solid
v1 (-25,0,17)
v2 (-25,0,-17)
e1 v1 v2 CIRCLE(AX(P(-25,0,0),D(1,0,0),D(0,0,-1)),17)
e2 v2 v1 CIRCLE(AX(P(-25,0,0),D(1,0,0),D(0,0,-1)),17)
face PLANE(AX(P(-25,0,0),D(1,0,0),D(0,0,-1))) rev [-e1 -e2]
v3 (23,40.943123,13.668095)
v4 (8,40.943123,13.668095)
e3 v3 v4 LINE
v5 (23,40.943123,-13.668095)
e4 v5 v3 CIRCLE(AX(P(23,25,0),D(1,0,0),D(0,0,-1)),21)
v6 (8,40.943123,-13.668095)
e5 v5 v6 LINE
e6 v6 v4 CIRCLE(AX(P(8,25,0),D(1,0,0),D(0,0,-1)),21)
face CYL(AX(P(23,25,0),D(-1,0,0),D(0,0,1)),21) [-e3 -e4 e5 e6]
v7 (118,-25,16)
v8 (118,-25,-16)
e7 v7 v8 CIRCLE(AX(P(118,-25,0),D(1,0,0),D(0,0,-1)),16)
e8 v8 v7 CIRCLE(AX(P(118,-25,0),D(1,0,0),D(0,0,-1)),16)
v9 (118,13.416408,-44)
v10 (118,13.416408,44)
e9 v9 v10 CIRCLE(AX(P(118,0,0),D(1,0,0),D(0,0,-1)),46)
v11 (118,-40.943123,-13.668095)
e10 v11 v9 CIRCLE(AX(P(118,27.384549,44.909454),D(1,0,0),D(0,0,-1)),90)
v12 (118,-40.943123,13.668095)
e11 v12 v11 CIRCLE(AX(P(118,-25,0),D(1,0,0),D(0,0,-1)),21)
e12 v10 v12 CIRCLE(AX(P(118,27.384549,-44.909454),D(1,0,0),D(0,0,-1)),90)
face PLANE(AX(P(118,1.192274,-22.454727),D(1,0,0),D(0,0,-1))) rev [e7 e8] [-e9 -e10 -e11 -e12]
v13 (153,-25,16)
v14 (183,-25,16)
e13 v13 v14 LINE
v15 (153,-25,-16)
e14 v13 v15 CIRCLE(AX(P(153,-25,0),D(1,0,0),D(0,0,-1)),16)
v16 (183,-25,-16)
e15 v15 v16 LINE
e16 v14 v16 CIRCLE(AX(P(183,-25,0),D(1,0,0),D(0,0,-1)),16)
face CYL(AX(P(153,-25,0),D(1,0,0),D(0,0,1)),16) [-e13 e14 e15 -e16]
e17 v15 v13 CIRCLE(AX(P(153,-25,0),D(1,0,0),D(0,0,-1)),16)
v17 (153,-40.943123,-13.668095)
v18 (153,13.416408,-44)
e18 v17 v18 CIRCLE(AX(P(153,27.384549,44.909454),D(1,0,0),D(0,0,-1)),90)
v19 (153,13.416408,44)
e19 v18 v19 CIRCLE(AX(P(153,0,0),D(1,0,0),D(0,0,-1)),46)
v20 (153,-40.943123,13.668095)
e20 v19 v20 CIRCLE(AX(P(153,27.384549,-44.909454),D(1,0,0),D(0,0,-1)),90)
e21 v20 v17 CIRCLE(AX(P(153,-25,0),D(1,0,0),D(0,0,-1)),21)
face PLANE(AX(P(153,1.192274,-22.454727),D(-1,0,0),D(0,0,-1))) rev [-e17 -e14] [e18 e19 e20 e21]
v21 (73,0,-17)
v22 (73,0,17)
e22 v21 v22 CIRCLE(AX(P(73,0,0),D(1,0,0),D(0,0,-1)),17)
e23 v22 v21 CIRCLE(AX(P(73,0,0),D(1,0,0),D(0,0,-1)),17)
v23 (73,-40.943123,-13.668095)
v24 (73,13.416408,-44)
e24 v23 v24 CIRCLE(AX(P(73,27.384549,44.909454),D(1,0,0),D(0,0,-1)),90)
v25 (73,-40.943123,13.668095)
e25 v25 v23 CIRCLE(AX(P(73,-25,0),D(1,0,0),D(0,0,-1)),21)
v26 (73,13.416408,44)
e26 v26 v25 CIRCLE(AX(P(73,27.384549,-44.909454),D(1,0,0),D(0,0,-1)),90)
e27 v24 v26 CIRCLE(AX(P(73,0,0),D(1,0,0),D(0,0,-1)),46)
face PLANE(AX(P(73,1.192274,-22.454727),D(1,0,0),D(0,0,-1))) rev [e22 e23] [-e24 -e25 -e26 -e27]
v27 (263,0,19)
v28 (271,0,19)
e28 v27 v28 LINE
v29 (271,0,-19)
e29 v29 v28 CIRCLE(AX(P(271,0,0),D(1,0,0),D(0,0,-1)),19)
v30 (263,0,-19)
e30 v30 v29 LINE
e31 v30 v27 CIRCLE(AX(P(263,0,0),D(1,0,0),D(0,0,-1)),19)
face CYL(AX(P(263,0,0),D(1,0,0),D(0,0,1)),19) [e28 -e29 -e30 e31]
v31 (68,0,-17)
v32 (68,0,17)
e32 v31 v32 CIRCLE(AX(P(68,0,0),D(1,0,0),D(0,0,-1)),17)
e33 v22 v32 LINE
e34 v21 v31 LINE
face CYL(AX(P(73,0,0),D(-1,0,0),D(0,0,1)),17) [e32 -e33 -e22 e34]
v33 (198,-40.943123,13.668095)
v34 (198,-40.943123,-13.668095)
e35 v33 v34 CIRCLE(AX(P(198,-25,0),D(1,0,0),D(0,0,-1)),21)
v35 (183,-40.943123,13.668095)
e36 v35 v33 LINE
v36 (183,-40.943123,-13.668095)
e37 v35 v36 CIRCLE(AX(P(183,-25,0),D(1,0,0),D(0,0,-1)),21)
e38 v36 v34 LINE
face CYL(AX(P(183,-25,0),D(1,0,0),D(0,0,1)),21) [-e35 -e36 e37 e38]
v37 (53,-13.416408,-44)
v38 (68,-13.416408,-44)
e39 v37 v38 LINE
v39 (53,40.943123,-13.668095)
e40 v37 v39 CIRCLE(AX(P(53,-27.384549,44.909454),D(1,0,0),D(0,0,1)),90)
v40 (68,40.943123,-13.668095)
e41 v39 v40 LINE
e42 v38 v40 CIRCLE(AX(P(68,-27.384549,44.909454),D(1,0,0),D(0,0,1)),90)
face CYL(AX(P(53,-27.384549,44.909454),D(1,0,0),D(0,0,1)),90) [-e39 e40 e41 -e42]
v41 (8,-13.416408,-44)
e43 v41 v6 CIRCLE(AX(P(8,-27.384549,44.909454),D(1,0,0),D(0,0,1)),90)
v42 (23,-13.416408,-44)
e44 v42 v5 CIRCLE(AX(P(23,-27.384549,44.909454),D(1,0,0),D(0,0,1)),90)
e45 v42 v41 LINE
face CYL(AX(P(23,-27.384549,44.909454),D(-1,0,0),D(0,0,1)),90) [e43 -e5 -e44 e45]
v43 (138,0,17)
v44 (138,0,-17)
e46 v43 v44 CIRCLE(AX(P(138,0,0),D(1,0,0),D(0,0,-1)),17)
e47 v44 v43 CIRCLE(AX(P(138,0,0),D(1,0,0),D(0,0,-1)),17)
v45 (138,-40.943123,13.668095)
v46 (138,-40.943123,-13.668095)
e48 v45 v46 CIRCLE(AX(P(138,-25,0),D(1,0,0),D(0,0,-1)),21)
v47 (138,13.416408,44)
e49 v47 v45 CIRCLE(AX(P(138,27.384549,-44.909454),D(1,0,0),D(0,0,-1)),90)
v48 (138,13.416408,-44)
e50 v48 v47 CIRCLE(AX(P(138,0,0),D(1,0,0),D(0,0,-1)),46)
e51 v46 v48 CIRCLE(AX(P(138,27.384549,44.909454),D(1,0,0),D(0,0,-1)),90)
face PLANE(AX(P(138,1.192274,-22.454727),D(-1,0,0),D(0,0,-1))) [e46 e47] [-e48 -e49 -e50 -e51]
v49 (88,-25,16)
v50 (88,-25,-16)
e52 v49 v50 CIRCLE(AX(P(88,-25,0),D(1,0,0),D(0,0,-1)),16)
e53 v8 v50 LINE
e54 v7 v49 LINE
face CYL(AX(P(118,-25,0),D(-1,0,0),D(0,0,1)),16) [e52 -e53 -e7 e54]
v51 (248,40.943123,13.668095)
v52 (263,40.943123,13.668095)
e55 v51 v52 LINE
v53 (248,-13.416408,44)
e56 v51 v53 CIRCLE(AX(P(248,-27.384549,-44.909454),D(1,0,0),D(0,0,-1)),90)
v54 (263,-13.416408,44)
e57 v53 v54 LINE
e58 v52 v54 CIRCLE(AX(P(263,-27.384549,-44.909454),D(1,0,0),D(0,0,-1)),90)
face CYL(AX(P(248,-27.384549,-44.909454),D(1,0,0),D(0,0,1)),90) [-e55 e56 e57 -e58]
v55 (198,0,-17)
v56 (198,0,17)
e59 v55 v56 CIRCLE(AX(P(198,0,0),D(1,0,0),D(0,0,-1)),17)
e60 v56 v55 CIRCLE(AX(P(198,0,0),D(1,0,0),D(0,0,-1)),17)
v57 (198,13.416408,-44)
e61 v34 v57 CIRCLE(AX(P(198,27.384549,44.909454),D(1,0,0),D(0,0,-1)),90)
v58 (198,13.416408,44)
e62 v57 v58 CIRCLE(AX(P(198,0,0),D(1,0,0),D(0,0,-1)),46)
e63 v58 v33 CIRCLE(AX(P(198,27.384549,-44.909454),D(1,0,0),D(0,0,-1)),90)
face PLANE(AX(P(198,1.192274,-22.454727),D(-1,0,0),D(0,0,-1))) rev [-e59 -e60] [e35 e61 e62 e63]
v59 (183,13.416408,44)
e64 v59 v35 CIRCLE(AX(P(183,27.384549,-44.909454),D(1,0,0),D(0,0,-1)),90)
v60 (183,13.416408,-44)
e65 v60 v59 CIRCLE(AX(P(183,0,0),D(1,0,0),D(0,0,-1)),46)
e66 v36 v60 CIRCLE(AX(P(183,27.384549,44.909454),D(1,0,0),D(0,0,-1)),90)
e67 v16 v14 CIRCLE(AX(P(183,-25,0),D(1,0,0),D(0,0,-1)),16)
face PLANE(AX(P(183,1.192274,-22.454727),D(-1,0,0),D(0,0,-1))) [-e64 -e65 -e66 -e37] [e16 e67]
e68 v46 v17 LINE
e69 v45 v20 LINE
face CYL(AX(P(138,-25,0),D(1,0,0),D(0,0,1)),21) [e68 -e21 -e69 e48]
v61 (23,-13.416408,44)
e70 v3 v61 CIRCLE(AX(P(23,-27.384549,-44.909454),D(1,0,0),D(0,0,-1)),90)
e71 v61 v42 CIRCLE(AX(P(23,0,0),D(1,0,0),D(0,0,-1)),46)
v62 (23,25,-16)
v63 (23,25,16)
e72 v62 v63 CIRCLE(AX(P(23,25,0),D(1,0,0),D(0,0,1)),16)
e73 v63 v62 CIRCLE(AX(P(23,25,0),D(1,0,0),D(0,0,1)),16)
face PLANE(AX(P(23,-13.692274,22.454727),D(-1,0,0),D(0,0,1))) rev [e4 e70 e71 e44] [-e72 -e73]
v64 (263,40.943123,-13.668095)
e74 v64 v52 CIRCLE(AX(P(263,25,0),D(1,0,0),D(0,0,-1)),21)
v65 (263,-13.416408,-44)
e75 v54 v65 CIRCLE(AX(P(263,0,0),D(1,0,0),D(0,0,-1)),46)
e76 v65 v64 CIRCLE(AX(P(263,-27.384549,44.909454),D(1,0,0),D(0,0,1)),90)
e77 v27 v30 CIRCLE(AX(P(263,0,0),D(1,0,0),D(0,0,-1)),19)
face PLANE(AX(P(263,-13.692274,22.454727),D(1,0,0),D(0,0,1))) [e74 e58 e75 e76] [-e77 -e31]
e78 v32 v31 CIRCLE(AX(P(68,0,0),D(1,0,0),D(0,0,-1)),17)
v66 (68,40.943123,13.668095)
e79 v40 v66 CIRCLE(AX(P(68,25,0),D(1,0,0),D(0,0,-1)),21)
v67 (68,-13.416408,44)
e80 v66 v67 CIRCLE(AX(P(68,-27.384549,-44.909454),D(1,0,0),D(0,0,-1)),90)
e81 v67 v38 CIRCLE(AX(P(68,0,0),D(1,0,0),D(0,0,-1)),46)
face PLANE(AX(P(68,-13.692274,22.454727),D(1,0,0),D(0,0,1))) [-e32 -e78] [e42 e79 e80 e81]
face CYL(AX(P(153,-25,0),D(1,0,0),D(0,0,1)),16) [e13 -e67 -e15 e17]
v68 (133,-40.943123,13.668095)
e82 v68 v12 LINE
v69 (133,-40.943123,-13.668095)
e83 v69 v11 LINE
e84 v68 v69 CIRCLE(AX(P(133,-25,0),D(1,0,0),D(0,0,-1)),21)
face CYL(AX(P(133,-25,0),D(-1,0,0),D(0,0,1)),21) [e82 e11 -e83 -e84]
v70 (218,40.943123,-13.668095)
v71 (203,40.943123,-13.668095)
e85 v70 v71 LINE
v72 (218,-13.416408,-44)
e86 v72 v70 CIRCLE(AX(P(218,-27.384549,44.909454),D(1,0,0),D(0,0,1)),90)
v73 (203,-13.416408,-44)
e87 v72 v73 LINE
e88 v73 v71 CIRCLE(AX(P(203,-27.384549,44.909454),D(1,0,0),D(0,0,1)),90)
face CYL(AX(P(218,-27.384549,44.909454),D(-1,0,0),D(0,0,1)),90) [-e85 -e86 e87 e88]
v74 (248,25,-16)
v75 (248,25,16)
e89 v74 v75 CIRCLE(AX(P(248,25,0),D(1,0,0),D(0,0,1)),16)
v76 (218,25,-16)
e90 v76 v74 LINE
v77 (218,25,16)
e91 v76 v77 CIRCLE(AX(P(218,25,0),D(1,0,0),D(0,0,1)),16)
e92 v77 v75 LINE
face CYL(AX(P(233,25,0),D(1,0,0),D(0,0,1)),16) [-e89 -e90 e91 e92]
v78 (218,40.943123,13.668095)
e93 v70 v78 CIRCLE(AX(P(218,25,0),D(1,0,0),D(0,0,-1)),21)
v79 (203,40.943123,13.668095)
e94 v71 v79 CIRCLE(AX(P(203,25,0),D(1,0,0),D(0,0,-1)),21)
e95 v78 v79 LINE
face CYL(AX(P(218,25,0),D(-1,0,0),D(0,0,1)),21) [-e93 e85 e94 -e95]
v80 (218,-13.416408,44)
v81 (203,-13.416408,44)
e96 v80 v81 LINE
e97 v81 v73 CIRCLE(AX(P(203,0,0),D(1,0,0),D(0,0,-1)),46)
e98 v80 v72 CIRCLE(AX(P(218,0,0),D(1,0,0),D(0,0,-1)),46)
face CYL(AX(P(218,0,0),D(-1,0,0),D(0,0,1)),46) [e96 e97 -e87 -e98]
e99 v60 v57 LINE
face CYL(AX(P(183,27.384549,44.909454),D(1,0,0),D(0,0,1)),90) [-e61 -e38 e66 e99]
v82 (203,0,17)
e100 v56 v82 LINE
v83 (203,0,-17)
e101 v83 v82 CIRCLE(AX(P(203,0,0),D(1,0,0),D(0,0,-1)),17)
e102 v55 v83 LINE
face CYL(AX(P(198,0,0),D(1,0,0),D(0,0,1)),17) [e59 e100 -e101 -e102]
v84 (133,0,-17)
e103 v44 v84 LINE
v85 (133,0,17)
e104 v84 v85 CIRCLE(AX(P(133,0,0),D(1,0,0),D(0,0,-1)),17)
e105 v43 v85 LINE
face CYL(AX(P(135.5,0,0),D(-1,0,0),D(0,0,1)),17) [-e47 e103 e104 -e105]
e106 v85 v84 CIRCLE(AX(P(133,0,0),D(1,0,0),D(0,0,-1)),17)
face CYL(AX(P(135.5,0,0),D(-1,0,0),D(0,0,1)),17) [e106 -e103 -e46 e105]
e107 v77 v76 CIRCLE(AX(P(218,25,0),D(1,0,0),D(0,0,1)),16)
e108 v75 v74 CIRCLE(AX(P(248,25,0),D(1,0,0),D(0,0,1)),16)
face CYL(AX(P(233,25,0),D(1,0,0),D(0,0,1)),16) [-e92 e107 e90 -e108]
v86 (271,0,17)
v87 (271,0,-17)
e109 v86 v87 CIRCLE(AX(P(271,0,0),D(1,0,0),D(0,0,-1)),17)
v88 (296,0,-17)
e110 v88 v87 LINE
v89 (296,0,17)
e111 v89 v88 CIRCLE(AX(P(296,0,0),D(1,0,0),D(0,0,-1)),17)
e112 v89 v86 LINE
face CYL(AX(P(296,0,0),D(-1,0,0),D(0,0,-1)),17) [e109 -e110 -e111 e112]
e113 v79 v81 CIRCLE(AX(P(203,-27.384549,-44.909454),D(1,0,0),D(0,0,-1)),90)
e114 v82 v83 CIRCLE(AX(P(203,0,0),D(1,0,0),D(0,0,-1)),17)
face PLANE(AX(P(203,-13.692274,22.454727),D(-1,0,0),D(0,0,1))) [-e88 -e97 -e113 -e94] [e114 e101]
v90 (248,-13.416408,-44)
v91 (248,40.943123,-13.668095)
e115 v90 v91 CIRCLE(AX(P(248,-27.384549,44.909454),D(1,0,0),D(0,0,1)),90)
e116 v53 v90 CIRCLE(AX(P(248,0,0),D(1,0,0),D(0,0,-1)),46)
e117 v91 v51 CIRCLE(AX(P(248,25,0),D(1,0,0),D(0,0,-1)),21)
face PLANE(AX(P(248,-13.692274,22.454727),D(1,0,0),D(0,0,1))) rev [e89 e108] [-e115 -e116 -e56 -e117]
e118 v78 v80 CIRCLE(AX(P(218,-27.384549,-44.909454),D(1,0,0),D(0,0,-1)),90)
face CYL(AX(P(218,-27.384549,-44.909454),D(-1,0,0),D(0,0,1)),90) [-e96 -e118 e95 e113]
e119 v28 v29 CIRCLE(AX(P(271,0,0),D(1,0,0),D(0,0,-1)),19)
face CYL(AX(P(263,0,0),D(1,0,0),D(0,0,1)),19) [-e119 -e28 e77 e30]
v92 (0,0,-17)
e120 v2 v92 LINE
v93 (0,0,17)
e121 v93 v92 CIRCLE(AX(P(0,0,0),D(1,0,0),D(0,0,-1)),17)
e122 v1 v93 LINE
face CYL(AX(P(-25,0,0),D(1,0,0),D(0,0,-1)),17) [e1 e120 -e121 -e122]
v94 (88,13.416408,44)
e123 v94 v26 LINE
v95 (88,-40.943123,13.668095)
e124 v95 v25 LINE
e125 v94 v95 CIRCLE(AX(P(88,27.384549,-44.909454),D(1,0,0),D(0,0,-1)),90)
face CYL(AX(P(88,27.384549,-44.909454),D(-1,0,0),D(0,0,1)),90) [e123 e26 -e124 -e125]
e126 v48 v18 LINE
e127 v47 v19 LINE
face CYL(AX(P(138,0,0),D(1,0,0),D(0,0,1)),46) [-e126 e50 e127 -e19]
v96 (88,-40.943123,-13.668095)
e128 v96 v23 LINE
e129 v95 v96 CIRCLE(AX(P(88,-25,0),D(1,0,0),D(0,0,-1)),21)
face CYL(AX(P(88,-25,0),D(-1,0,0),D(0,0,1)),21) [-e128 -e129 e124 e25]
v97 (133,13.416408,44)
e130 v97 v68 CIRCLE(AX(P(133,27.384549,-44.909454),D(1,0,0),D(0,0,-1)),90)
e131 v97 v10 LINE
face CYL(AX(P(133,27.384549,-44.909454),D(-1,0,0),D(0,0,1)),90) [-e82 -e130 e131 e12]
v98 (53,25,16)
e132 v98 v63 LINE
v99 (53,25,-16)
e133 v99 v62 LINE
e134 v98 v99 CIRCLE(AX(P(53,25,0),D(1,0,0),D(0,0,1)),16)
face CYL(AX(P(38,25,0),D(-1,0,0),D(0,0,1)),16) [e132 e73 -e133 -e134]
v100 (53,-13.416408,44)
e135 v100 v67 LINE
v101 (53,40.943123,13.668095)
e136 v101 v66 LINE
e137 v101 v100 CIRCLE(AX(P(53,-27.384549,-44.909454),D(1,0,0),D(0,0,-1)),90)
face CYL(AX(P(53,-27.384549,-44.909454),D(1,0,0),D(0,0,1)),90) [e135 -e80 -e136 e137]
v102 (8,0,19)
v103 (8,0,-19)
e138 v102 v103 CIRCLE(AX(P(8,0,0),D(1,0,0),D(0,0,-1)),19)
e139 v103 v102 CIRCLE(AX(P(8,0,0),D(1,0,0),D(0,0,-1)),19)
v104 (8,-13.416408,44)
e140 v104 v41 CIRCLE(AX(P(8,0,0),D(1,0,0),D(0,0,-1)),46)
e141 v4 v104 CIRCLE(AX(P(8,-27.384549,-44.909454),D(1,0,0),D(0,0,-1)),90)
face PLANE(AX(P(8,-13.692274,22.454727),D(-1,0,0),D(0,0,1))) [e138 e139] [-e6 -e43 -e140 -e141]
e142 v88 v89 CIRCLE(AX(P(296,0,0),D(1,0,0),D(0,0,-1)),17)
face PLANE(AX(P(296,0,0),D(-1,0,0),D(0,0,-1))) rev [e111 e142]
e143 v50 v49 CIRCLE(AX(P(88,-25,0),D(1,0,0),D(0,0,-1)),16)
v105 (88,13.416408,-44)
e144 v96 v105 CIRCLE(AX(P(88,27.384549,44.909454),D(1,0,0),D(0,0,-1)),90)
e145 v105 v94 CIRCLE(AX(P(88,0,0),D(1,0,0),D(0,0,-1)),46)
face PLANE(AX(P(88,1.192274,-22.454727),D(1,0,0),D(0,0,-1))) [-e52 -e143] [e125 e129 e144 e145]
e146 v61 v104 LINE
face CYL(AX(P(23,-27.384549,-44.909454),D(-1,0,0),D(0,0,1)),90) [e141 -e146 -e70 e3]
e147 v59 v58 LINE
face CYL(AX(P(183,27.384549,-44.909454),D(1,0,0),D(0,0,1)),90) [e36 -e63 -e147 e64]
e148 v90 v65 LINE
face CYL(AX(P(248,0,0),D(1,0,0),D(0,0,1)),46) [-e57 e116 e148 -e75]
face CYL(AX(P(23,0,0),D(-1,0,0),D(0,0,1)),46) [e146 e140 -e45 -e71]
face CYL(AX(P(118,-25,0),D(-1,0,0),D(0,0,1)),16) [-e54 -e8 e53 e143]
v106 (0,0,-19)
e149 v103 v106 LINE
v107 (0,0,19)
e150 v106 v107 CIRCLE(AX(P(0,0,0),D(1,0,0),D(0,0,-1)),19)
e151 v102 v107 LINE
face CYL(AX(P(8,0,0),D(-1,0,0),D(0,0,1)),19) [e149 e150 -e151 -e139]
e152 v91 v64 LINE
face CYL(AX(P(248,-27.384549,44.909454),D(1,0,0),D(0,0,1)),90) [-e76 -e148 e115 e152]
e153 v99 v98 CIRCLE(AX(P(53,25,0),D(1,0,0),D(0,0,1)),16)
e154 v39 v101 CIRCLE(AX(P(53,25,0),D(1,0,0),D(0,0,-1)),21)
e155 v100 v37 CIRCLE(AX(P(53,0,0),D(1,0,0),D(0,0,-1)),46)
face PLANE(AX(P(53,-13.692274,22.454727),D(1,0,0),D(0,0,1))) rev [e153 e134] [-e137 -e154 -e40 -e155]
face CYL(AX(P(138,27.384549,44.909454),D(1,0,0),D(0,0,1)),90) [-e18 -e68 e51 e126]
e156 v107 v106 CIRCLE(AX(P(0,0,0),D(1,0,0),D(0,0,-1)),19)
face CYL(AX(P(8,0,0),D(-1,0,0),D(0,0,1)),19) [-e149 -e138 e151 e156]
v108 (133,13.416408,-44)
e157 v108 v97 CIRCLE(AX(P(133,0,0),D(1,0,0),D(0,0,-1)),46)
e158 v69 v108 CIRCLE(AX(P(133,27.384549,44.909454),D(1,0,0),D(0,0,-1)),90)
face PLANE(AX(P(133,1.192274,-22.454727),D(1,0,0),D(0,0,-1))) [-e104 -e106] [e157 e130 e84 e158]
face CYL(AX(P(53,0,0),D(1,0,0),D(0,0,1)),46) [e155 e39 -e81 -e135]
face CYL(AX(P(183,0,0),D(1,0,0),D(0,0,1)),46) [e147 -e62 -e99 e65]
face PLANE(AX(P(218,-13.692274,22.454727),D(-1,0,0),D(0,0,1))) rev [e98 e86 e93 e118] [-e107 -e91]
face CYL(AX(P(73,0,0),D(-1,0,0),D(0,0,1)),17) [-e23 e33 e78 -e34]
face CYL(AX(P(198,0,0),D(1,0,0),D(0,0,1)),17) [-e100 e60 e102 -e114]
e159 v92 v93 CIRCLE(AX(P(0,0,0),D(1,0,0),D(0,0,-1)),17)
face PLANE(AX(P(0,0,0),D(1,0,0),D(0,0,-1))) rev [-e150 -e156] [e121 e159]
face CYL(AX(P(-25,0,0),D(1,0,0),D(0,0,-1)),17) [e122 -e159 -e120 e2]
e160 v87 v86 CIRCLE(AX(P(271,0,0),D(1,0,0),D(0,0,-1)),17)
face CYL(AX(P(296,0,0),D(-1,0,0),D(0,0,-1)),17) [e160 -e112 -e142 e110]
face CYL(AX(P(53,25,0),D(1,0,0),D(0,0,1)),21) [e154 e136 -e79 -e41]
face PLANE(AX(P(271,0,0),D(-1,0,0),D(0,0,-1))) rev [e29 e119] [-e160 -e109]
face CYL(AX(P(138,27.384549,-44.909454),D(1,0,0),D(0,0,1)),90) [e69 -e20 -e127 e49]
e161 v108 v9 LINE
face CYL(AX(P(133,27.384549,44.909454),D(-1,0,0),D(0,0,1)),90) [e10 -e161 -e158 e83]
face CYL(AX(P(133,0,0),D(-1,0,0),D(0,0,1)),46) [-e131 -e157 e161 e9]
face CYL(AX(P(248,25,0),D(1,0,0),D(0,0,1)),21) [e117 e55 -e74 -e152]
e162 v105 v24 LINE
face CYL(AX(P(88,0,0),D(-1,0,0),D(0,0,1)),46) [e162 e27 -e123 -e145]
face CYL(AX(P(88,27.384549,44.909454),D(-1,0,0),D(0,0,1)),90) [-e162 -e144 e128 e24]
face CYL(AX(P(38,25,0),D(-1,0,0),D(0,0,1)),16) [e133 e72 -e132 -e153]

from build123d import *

# Parameters (mm, degrees)
END_JOURNAL_PROFILE_R         = 17
END_JOURNAL_34_DEPTH          = 25
SKETCH1_3_R                   = 19
JOURNAL_COLLAR_38_DEPTH       = 8
CRANK_WEB_1_DEPTH             = 15
CRANK_PIN_1_PROFILE_R         = 16
CRANK_PIN_1_32_DEPTH          = 15
MAIN_START                    = 5
MAIN_JOURNAL_SPACER_PROFILE_R = 17
MAIN_JOURNAL_SPACER_34_DEPTH  = 5
CRANK_WEB_3_DEPTH             = 15
CRANK_PIN_2_PROFILE_R         = 16
CRANK_PIN_2_32_DEPTH          = 30
CRANK_WEB_4_DEPTH             = 15
CENTRE_START                  = 2.5
CENTRE_JOURNAL_PROFILE_R      = 17
CENTRE_JOURNAL_HALF_34_DEPTH  = 2.5


with BuildPart() as part:
    # End Journal Profile → End Journal _34 (new body)
    with BuildSketch(Plane(origin=(0, 0, 0), x_dir=(0, 0, -1), z_dir=(1, 0, 0))):
        Circle(END_JOURNAL_PROFILE_R)
    extrude(amount=-END_JOURNAL_34_DEPTH)

    # Sketch1_3 → Journal Collar _38 (add)
    with BuildSketch(Plane(origin=(0, 0, 0), x_dir=(0, 0, -1), z_dir=(1, 0, 0))):
        Circle(SKETCH1_3_R)
    extrude(amount=JOURNAL_COLLAR_38_DEPTH)

    # Crank Web 1 Profile → Crank Web 1 (add)
    with BuildSketch(Plane(origin=(8, 0, 0), x_dir=(0, 0, -1), z_dir=(1, 0, 0))):
        with BuildLine():
            ThreePointArc((13.668094758, 40.943123461), (0, 46), (-13.668094758, 40.943123461))
            ThreePointArc((-13.668094758, 40.943123461), (-33.683444249, 16.469257624), (-44, -13.416407865))
            ThreePointArc((-44, -13.416407865), (0, -46), (44, -13.416407865))
            ThreePointArc((44, -13.416407865), (33.683444249, 16.469257624), (13.668094758, 40.943123461))
        make_face()
    crank_web_1 = extrude(amount=CRANK_WEB_1_DEPTH)

    # Crank Pin 1 Profile → Crank Pin 1 _32 (add)
    with BuildSketch(Plane(origin=(23, 0, 0), x_dir=(0, 0, -1), z_dir=(1, 0, 0))):
        with Locations(Location((0, 25, 0), (0, 0, 180))):
            Circle(CRANK_PIN_1_PROFILE_R)
    crank_pin_1_32 = extrude(amount=CRANK_PIN_1_32_DEPTH)

    # Crank Web 2 Mirror: Crank Web 1, Crank Pin 1 _32 across plane
    add(crank_web_1.mirror(Plane(origin=(38, 25, 0), x_dir=(0, 0, 1), z_dir=(1, 0, 0))))
    add(crank_pin_1_32.mirror(Plane(origin=(38, 25, 0), x_dir=(0, 0, 1), z_dir=(1, 0, 0))))

    # Main Journal Spacer Profile → Main Journal Spacer _34 (add)
    with BuildSketch(Plane(origin=(68, 0, 0), x_dir=(0, 0, -1), z_dir=(1, 0, 0)).offset(MAIN_START)):
        Circle(MAIN_JOURNAL_SPACER_PROFILE_R)
    extrude(amount=-MAIN_JOURNAL_SPACER_34_DEPTH)

    # Crank Web 3 Profile → Crank Web 3 (add)
    with BuildSketch(Plane(origin=(73, 0, 0), x_dir=(0, 0, -1), z_dir=(1, 0, 0))):
        with BuildLine():
            ThreePointArc((-13.668094758, -40.943123461), (0, -46), (13.668094758, -40.943123461))
            ThreePointArc((13.668094758, -40.943123461), (33.683444249, -16.469257624), (44, 13.416407865))
            ThreePointArc((44, 13.416407865), (0, 46), (-44, 13.416407865))
            ThreePointArc((-44, 13.416407865), (-33.683444249, -16.469257624), (-13.668094758, -40.943123461))
        make_face()
    extrude(amount=CRANK_WEB_3_DEPTH)

    # Crank Pin 2 Profile → Crank Pin 2 _32 (add)
    with BuildSketch(Plane(origin=(88, 0, 0), x_dir=(0, 0, -1), z_dir=(1, 0, 0))):
        with Locations((0, -25)):
            Circle(CRANK_PIN_2_PROFILE_R)
    extrude(amount=CRANK_PIN_2_32_DEPTH)

    # Crank Web 4 Profile → Crank Web 4 (add)
    with BuildSketch(Plane(origin=(118, 0, 0), x_dir=(0, 0, -1), z_dir=(1, 0, 0))):
        with BuildLine():
            ThreePointArc((-13.668094758, -40.943123461), (0, -46), (13.668094758, -40.943123461))
            ThreePointArc((13.668094758, -40.943123461), (33.683444249, -16.469257624), (44, 13.416407865))
            ThreePointArc((44, 13.416407865), (0, 46), (-44, 13.416407865))
            ThreePointArc((-44, 13.416407865), (-33.683444249, -16.469257624), (-13.668094758, -40.943123461))
        make_face()
    extrude(amount=CRANK_WEB_4_DEPTH)

    # Centre Journal Profile → Centre Journal Half _34 (add)
    with BuildSketch(Plane(origin=(133, 0, 0), x_dir=(0, 0, -1), z_dir=(1, 0, 0)).offset(CENTRE_START)):
        Circle(CENTRE_JOURNAL_PROFILE_R)
    extrude(amount=-CENTRE_JOURNAL_HALF_34_DEPTH)

    # Crankshaft Half Mirror: part across plane


with BuildPart() as part_1:
    add(part.part)
    add(part.part.mirror(Plane(origin=(135.5, 0, 0), x_dir=(0, 0, 1), z_dir=(1, 0, 0))))


solid = part_1.part
